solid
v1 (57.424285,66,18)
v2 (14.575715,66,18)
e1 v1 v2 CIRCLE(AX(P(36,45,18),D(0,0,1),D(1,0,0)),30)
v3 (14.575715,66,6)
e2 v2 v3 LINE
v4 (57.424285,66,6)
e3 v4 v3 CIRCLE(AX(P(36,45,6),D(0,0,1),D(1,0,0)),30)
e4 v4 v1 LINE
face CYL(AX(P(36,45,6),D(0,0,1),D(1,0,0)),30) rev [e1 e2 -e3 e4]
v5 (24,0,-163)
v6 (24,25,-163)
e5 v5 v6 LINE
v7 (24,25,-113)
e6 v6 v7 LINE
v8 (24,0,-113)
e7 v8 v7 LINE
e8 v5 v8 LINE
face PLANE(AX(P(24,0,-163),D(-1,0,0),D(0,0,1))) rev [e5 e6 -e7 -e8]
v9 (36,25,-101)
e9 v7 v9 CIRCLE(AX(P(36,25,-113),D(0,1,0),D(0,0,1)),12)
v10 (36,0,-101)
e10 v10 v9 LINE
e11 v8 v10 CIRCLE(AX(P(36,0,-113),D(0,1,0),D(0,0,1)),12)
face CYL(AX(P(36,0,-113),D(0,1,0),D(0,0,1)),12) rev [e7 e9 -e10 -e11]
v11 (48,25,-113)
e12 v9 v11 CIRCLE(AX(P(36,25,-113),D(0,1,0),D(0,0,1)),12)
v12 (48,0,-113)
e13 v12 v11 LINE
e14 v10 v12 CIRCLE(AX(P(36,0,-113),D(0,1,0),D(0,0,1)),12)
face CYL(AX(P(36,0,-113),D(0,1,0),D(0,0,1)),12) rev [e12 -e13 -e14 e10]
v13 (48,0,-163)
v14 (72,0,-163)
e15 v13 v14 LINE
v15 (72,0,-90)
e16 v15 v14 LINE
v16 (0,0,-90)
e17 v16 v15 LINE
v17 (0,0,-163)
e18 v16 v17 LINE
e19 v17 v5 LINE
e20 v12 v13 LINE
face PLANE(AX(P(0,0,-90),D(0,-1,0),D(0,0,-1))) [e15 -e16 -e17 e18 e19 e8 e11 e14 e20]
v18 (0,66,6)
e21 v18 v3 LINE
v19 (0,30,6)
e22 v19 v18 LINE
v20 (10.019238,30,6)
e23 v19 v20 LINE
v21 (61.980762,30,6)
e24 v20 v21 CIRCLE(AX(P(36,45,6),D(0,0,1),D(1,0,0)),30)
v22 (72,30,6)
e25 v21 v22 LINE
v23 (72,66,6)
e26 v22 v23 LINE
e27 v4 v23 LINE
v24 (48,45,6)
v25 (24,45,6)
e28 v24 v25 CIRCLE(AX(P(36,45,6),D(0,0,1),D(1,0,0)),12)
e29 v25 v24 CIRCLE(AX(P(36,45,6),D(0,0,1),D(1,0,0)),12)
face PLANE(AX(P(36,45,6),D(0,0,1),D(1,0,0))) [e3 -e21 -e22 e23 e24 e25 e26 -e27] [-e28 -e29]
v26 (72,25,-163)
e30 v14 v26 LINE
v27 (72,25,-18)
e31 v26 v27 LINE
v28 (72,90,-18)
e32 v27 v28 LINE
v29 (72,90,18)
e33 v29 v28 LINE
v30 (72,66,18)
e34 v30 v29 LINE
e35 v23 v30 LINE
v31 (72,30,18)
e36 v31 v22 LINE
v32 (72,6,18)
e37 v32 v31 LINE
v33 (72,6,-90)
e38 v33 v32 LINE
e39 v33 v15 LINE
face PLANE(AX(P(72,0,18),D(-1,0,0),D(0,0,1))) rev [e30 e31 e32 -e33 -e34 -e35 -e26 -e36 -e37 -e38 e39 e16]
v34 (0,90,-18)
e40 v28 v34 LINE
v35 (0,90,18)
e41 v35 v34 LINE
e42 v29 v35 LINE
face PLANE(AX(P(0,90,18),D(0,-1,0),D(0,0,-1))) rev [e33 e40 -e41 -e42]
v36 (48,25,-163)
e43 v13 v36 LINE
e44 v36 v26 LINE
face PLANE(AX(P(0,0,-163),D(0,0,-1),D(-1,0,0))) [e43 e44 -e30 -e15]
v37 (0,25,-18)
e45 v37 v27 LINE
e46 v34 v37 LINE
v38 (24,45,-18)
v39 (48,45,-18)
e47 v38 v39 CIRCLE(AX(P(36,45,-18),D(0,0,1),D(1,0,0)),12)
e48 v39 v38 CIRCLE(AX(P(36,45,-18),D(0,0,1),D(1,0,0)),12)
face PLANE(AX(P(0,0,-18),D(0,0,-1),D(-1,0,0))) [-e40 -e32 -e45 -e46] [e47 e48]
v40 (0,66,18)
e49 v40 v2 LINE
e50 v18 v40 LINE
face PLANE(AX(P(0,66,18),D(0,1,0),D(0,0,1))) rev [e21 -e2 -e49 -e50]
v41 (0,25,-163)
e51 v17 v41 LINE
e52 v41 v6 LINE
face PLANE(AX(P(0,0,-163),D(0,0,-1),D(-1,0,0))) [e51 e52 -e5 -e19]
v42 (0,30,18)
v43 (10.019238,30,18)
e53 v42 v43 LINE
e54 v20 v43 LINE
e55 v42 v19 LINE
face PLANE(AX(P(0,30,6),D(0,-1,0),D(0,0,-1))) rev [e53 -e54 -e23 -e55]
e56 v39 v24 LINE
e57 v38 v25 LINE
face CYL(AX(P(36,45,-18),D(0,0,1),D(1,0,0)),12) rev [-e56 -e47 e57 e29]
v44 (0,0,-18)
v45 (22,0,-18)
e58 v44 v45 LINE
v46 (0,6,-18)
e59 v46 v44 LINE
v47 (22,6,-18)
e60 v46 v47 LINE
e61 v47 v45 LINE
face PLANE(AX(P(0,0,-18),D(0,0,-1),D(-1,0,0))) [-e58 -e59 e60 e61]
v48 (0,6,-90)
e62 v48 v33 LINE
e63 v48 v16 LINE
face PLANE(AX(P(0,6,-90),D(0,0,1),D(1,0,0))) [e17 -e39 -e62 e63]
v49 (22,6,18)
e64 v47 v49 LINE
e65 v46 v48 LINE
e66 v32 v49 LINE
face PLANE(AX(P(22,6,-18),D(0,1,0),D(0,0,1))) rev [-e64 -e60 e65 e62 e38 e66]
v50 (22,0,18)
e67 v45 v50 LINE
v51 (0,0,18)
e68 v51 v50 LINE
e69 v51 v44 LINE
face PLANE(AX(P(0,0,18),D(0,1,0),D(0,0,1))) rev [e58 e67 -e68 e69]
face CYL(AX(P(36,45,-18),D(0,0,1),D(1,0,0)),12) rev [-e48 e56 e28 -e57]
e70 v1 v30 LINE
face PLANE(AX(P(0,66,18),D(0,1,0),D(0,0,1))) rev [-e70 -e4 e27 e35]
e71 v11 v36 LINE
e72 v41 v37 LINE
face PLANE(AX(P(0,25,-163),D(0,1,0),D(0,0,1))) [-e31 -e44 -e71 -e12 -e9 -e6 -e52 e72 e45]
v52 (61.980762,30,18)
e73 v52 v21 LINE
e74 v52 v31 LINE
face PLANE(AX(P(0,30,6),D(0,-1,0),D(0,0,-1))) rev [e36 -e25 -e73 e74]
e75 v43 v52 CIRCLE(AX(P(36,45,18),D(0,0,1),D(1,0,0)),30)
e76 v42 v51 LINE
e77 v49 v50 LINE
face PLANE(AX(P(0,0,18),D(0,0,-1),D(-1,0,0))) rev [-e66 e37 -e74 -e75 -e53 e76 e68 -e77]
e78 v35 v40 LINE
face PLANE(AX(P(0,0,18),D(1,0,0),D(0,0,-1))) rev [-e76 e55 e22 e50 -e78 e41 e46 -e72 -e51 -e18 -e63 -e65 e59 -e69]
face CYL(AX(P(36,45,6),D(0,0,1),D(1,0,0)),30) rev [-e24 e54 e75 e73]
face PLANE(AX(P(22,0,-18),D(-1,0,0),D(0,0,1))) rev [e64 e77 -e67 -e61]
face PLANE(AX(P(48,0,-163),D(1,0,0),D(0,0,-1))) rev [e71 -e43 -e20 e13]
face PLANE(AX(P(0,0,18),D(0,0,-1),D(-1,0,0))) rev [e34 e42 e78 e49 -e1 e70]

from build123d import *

# Parameters (mm, degrees)
BASE_BLOCK_SKETCH_W       = 72
BASE_BLOCK_SKETCH_H       = 90
BASE_BLOCK_90X72X36_DEPTH = 18
ARC_RECESS_SKETCH_R       = 30
ARC_RECESS_60_DEPTH       = 12
BORE_24_DEPTH             = 117.653332571
RECESS_RELIEF_SKETCH_R    = 12
RECESS_RELIEF_CUT_DEPTH   = 118.728501222
BOTTOM_GROOVE_SKETCH_W    = 50
BOTTOM_GROOVE_SKETCH_H    = 6
BOTTOM_GROOVE_6X50_DEPTH  = 121.747670785
FORK_ARM_DEPTH            = 72
FORK_SLOT_24_DEPTH        = 190.67867566


with BuildPart() as part:
    # Base Block Sketch → Base Block 90x72x36 (new, symmetric)
    with BuildSketch(Plane.XY):
        with Locations((36, 45)):
            Rectangle(BASE_BLOCK_SKETCH_W, BASE_BLOCK_SKETCH_H)
    extrude(amount=BASE_BLOCK_90X72X36_DEPTH, both=True)

    # Arc Recess Sketch → Arc Recess Ø60 (cut)
    with BuildSketch(Plane.XY.offset(18)):
        with Locations((36, 45)):
            Circle(ARC_RECESS_SKETCH_R)
    extrude(amount=-ARC_RECESS_60_DEPTH, mode=Mode.SUBTRACT)

    # Bore Sketch → Bore Ø24 (cut, through all)
    with BuildSketch(Plane(origin=(72, 0, 0), x_dir=(0, 0, -1), z_dir=(1, 0, 0))):
        Polygon((-18, 66), (-6, 66), (-6, 45), (-6, 30), (-18, 30), align=None)
    extrude(amount=-BORE_24_DEPTH, mode=Mode.SUBTRACT)

    # Recess Relief Sketch → Recess Relief Cut (cut, through all)
    with BuildSketch(Plane.XY.offset(6)):
        with Locations((36, 45)):
            Circle(RECESS_RELIEF_SKETCH_R)
    extrude(amount=-RECESS_RELIEF_CUT_DEPTH, mode=Mode.SUBTRACT)

    # Bottom Groove Sketch → Bottom Groove 6x50 (cut, through all)
    with BuildSketch(Plane.XY.offset(18)):
        with Locations((47, 3)):
            Rectangle(BOTTOM_GROOVE_SKETCH_W, BOTTOM_GROOVE_SKETCH_H)
    extrude(amount=-BOTTOM_GROOVE_6X50_DEPTH, mode=Mode.SUBTRACT)

    # Fork Arm Sketch → Fork Arm (add)
    with BuildSketch(Plane(origin=(72, 0, 0), x_dir=(0, 0, -1), z_dir=(1, 0, 0))):
        Polygon((18, 6), (90, 6), (90, 0), (163, 0), (163, 25), (18, 25), align=None)
    extrude(amount=-FORK_ARM_DEPTH)

    # Fork Slot Sketch → Fork Slot 24 (cut, through all)
    with BuildSketch(Plane(origin=(0, 25, 0), x_dir=(1, 0, 0), z_dir=(0, 1, 0))):
        with BuildLine():
            Line((48, 163), (48, 113))
            ThreePointArc((48, 113), (36, 101), (24, 113))
            Line((24, 113), (24, 163))
            Line((24, 163), (48, 163))
        make_face()
    extrude(amount=-FORK_SLOT_24_DEPTH, mode=Mode.SUBTRACT)


solid = part.part
